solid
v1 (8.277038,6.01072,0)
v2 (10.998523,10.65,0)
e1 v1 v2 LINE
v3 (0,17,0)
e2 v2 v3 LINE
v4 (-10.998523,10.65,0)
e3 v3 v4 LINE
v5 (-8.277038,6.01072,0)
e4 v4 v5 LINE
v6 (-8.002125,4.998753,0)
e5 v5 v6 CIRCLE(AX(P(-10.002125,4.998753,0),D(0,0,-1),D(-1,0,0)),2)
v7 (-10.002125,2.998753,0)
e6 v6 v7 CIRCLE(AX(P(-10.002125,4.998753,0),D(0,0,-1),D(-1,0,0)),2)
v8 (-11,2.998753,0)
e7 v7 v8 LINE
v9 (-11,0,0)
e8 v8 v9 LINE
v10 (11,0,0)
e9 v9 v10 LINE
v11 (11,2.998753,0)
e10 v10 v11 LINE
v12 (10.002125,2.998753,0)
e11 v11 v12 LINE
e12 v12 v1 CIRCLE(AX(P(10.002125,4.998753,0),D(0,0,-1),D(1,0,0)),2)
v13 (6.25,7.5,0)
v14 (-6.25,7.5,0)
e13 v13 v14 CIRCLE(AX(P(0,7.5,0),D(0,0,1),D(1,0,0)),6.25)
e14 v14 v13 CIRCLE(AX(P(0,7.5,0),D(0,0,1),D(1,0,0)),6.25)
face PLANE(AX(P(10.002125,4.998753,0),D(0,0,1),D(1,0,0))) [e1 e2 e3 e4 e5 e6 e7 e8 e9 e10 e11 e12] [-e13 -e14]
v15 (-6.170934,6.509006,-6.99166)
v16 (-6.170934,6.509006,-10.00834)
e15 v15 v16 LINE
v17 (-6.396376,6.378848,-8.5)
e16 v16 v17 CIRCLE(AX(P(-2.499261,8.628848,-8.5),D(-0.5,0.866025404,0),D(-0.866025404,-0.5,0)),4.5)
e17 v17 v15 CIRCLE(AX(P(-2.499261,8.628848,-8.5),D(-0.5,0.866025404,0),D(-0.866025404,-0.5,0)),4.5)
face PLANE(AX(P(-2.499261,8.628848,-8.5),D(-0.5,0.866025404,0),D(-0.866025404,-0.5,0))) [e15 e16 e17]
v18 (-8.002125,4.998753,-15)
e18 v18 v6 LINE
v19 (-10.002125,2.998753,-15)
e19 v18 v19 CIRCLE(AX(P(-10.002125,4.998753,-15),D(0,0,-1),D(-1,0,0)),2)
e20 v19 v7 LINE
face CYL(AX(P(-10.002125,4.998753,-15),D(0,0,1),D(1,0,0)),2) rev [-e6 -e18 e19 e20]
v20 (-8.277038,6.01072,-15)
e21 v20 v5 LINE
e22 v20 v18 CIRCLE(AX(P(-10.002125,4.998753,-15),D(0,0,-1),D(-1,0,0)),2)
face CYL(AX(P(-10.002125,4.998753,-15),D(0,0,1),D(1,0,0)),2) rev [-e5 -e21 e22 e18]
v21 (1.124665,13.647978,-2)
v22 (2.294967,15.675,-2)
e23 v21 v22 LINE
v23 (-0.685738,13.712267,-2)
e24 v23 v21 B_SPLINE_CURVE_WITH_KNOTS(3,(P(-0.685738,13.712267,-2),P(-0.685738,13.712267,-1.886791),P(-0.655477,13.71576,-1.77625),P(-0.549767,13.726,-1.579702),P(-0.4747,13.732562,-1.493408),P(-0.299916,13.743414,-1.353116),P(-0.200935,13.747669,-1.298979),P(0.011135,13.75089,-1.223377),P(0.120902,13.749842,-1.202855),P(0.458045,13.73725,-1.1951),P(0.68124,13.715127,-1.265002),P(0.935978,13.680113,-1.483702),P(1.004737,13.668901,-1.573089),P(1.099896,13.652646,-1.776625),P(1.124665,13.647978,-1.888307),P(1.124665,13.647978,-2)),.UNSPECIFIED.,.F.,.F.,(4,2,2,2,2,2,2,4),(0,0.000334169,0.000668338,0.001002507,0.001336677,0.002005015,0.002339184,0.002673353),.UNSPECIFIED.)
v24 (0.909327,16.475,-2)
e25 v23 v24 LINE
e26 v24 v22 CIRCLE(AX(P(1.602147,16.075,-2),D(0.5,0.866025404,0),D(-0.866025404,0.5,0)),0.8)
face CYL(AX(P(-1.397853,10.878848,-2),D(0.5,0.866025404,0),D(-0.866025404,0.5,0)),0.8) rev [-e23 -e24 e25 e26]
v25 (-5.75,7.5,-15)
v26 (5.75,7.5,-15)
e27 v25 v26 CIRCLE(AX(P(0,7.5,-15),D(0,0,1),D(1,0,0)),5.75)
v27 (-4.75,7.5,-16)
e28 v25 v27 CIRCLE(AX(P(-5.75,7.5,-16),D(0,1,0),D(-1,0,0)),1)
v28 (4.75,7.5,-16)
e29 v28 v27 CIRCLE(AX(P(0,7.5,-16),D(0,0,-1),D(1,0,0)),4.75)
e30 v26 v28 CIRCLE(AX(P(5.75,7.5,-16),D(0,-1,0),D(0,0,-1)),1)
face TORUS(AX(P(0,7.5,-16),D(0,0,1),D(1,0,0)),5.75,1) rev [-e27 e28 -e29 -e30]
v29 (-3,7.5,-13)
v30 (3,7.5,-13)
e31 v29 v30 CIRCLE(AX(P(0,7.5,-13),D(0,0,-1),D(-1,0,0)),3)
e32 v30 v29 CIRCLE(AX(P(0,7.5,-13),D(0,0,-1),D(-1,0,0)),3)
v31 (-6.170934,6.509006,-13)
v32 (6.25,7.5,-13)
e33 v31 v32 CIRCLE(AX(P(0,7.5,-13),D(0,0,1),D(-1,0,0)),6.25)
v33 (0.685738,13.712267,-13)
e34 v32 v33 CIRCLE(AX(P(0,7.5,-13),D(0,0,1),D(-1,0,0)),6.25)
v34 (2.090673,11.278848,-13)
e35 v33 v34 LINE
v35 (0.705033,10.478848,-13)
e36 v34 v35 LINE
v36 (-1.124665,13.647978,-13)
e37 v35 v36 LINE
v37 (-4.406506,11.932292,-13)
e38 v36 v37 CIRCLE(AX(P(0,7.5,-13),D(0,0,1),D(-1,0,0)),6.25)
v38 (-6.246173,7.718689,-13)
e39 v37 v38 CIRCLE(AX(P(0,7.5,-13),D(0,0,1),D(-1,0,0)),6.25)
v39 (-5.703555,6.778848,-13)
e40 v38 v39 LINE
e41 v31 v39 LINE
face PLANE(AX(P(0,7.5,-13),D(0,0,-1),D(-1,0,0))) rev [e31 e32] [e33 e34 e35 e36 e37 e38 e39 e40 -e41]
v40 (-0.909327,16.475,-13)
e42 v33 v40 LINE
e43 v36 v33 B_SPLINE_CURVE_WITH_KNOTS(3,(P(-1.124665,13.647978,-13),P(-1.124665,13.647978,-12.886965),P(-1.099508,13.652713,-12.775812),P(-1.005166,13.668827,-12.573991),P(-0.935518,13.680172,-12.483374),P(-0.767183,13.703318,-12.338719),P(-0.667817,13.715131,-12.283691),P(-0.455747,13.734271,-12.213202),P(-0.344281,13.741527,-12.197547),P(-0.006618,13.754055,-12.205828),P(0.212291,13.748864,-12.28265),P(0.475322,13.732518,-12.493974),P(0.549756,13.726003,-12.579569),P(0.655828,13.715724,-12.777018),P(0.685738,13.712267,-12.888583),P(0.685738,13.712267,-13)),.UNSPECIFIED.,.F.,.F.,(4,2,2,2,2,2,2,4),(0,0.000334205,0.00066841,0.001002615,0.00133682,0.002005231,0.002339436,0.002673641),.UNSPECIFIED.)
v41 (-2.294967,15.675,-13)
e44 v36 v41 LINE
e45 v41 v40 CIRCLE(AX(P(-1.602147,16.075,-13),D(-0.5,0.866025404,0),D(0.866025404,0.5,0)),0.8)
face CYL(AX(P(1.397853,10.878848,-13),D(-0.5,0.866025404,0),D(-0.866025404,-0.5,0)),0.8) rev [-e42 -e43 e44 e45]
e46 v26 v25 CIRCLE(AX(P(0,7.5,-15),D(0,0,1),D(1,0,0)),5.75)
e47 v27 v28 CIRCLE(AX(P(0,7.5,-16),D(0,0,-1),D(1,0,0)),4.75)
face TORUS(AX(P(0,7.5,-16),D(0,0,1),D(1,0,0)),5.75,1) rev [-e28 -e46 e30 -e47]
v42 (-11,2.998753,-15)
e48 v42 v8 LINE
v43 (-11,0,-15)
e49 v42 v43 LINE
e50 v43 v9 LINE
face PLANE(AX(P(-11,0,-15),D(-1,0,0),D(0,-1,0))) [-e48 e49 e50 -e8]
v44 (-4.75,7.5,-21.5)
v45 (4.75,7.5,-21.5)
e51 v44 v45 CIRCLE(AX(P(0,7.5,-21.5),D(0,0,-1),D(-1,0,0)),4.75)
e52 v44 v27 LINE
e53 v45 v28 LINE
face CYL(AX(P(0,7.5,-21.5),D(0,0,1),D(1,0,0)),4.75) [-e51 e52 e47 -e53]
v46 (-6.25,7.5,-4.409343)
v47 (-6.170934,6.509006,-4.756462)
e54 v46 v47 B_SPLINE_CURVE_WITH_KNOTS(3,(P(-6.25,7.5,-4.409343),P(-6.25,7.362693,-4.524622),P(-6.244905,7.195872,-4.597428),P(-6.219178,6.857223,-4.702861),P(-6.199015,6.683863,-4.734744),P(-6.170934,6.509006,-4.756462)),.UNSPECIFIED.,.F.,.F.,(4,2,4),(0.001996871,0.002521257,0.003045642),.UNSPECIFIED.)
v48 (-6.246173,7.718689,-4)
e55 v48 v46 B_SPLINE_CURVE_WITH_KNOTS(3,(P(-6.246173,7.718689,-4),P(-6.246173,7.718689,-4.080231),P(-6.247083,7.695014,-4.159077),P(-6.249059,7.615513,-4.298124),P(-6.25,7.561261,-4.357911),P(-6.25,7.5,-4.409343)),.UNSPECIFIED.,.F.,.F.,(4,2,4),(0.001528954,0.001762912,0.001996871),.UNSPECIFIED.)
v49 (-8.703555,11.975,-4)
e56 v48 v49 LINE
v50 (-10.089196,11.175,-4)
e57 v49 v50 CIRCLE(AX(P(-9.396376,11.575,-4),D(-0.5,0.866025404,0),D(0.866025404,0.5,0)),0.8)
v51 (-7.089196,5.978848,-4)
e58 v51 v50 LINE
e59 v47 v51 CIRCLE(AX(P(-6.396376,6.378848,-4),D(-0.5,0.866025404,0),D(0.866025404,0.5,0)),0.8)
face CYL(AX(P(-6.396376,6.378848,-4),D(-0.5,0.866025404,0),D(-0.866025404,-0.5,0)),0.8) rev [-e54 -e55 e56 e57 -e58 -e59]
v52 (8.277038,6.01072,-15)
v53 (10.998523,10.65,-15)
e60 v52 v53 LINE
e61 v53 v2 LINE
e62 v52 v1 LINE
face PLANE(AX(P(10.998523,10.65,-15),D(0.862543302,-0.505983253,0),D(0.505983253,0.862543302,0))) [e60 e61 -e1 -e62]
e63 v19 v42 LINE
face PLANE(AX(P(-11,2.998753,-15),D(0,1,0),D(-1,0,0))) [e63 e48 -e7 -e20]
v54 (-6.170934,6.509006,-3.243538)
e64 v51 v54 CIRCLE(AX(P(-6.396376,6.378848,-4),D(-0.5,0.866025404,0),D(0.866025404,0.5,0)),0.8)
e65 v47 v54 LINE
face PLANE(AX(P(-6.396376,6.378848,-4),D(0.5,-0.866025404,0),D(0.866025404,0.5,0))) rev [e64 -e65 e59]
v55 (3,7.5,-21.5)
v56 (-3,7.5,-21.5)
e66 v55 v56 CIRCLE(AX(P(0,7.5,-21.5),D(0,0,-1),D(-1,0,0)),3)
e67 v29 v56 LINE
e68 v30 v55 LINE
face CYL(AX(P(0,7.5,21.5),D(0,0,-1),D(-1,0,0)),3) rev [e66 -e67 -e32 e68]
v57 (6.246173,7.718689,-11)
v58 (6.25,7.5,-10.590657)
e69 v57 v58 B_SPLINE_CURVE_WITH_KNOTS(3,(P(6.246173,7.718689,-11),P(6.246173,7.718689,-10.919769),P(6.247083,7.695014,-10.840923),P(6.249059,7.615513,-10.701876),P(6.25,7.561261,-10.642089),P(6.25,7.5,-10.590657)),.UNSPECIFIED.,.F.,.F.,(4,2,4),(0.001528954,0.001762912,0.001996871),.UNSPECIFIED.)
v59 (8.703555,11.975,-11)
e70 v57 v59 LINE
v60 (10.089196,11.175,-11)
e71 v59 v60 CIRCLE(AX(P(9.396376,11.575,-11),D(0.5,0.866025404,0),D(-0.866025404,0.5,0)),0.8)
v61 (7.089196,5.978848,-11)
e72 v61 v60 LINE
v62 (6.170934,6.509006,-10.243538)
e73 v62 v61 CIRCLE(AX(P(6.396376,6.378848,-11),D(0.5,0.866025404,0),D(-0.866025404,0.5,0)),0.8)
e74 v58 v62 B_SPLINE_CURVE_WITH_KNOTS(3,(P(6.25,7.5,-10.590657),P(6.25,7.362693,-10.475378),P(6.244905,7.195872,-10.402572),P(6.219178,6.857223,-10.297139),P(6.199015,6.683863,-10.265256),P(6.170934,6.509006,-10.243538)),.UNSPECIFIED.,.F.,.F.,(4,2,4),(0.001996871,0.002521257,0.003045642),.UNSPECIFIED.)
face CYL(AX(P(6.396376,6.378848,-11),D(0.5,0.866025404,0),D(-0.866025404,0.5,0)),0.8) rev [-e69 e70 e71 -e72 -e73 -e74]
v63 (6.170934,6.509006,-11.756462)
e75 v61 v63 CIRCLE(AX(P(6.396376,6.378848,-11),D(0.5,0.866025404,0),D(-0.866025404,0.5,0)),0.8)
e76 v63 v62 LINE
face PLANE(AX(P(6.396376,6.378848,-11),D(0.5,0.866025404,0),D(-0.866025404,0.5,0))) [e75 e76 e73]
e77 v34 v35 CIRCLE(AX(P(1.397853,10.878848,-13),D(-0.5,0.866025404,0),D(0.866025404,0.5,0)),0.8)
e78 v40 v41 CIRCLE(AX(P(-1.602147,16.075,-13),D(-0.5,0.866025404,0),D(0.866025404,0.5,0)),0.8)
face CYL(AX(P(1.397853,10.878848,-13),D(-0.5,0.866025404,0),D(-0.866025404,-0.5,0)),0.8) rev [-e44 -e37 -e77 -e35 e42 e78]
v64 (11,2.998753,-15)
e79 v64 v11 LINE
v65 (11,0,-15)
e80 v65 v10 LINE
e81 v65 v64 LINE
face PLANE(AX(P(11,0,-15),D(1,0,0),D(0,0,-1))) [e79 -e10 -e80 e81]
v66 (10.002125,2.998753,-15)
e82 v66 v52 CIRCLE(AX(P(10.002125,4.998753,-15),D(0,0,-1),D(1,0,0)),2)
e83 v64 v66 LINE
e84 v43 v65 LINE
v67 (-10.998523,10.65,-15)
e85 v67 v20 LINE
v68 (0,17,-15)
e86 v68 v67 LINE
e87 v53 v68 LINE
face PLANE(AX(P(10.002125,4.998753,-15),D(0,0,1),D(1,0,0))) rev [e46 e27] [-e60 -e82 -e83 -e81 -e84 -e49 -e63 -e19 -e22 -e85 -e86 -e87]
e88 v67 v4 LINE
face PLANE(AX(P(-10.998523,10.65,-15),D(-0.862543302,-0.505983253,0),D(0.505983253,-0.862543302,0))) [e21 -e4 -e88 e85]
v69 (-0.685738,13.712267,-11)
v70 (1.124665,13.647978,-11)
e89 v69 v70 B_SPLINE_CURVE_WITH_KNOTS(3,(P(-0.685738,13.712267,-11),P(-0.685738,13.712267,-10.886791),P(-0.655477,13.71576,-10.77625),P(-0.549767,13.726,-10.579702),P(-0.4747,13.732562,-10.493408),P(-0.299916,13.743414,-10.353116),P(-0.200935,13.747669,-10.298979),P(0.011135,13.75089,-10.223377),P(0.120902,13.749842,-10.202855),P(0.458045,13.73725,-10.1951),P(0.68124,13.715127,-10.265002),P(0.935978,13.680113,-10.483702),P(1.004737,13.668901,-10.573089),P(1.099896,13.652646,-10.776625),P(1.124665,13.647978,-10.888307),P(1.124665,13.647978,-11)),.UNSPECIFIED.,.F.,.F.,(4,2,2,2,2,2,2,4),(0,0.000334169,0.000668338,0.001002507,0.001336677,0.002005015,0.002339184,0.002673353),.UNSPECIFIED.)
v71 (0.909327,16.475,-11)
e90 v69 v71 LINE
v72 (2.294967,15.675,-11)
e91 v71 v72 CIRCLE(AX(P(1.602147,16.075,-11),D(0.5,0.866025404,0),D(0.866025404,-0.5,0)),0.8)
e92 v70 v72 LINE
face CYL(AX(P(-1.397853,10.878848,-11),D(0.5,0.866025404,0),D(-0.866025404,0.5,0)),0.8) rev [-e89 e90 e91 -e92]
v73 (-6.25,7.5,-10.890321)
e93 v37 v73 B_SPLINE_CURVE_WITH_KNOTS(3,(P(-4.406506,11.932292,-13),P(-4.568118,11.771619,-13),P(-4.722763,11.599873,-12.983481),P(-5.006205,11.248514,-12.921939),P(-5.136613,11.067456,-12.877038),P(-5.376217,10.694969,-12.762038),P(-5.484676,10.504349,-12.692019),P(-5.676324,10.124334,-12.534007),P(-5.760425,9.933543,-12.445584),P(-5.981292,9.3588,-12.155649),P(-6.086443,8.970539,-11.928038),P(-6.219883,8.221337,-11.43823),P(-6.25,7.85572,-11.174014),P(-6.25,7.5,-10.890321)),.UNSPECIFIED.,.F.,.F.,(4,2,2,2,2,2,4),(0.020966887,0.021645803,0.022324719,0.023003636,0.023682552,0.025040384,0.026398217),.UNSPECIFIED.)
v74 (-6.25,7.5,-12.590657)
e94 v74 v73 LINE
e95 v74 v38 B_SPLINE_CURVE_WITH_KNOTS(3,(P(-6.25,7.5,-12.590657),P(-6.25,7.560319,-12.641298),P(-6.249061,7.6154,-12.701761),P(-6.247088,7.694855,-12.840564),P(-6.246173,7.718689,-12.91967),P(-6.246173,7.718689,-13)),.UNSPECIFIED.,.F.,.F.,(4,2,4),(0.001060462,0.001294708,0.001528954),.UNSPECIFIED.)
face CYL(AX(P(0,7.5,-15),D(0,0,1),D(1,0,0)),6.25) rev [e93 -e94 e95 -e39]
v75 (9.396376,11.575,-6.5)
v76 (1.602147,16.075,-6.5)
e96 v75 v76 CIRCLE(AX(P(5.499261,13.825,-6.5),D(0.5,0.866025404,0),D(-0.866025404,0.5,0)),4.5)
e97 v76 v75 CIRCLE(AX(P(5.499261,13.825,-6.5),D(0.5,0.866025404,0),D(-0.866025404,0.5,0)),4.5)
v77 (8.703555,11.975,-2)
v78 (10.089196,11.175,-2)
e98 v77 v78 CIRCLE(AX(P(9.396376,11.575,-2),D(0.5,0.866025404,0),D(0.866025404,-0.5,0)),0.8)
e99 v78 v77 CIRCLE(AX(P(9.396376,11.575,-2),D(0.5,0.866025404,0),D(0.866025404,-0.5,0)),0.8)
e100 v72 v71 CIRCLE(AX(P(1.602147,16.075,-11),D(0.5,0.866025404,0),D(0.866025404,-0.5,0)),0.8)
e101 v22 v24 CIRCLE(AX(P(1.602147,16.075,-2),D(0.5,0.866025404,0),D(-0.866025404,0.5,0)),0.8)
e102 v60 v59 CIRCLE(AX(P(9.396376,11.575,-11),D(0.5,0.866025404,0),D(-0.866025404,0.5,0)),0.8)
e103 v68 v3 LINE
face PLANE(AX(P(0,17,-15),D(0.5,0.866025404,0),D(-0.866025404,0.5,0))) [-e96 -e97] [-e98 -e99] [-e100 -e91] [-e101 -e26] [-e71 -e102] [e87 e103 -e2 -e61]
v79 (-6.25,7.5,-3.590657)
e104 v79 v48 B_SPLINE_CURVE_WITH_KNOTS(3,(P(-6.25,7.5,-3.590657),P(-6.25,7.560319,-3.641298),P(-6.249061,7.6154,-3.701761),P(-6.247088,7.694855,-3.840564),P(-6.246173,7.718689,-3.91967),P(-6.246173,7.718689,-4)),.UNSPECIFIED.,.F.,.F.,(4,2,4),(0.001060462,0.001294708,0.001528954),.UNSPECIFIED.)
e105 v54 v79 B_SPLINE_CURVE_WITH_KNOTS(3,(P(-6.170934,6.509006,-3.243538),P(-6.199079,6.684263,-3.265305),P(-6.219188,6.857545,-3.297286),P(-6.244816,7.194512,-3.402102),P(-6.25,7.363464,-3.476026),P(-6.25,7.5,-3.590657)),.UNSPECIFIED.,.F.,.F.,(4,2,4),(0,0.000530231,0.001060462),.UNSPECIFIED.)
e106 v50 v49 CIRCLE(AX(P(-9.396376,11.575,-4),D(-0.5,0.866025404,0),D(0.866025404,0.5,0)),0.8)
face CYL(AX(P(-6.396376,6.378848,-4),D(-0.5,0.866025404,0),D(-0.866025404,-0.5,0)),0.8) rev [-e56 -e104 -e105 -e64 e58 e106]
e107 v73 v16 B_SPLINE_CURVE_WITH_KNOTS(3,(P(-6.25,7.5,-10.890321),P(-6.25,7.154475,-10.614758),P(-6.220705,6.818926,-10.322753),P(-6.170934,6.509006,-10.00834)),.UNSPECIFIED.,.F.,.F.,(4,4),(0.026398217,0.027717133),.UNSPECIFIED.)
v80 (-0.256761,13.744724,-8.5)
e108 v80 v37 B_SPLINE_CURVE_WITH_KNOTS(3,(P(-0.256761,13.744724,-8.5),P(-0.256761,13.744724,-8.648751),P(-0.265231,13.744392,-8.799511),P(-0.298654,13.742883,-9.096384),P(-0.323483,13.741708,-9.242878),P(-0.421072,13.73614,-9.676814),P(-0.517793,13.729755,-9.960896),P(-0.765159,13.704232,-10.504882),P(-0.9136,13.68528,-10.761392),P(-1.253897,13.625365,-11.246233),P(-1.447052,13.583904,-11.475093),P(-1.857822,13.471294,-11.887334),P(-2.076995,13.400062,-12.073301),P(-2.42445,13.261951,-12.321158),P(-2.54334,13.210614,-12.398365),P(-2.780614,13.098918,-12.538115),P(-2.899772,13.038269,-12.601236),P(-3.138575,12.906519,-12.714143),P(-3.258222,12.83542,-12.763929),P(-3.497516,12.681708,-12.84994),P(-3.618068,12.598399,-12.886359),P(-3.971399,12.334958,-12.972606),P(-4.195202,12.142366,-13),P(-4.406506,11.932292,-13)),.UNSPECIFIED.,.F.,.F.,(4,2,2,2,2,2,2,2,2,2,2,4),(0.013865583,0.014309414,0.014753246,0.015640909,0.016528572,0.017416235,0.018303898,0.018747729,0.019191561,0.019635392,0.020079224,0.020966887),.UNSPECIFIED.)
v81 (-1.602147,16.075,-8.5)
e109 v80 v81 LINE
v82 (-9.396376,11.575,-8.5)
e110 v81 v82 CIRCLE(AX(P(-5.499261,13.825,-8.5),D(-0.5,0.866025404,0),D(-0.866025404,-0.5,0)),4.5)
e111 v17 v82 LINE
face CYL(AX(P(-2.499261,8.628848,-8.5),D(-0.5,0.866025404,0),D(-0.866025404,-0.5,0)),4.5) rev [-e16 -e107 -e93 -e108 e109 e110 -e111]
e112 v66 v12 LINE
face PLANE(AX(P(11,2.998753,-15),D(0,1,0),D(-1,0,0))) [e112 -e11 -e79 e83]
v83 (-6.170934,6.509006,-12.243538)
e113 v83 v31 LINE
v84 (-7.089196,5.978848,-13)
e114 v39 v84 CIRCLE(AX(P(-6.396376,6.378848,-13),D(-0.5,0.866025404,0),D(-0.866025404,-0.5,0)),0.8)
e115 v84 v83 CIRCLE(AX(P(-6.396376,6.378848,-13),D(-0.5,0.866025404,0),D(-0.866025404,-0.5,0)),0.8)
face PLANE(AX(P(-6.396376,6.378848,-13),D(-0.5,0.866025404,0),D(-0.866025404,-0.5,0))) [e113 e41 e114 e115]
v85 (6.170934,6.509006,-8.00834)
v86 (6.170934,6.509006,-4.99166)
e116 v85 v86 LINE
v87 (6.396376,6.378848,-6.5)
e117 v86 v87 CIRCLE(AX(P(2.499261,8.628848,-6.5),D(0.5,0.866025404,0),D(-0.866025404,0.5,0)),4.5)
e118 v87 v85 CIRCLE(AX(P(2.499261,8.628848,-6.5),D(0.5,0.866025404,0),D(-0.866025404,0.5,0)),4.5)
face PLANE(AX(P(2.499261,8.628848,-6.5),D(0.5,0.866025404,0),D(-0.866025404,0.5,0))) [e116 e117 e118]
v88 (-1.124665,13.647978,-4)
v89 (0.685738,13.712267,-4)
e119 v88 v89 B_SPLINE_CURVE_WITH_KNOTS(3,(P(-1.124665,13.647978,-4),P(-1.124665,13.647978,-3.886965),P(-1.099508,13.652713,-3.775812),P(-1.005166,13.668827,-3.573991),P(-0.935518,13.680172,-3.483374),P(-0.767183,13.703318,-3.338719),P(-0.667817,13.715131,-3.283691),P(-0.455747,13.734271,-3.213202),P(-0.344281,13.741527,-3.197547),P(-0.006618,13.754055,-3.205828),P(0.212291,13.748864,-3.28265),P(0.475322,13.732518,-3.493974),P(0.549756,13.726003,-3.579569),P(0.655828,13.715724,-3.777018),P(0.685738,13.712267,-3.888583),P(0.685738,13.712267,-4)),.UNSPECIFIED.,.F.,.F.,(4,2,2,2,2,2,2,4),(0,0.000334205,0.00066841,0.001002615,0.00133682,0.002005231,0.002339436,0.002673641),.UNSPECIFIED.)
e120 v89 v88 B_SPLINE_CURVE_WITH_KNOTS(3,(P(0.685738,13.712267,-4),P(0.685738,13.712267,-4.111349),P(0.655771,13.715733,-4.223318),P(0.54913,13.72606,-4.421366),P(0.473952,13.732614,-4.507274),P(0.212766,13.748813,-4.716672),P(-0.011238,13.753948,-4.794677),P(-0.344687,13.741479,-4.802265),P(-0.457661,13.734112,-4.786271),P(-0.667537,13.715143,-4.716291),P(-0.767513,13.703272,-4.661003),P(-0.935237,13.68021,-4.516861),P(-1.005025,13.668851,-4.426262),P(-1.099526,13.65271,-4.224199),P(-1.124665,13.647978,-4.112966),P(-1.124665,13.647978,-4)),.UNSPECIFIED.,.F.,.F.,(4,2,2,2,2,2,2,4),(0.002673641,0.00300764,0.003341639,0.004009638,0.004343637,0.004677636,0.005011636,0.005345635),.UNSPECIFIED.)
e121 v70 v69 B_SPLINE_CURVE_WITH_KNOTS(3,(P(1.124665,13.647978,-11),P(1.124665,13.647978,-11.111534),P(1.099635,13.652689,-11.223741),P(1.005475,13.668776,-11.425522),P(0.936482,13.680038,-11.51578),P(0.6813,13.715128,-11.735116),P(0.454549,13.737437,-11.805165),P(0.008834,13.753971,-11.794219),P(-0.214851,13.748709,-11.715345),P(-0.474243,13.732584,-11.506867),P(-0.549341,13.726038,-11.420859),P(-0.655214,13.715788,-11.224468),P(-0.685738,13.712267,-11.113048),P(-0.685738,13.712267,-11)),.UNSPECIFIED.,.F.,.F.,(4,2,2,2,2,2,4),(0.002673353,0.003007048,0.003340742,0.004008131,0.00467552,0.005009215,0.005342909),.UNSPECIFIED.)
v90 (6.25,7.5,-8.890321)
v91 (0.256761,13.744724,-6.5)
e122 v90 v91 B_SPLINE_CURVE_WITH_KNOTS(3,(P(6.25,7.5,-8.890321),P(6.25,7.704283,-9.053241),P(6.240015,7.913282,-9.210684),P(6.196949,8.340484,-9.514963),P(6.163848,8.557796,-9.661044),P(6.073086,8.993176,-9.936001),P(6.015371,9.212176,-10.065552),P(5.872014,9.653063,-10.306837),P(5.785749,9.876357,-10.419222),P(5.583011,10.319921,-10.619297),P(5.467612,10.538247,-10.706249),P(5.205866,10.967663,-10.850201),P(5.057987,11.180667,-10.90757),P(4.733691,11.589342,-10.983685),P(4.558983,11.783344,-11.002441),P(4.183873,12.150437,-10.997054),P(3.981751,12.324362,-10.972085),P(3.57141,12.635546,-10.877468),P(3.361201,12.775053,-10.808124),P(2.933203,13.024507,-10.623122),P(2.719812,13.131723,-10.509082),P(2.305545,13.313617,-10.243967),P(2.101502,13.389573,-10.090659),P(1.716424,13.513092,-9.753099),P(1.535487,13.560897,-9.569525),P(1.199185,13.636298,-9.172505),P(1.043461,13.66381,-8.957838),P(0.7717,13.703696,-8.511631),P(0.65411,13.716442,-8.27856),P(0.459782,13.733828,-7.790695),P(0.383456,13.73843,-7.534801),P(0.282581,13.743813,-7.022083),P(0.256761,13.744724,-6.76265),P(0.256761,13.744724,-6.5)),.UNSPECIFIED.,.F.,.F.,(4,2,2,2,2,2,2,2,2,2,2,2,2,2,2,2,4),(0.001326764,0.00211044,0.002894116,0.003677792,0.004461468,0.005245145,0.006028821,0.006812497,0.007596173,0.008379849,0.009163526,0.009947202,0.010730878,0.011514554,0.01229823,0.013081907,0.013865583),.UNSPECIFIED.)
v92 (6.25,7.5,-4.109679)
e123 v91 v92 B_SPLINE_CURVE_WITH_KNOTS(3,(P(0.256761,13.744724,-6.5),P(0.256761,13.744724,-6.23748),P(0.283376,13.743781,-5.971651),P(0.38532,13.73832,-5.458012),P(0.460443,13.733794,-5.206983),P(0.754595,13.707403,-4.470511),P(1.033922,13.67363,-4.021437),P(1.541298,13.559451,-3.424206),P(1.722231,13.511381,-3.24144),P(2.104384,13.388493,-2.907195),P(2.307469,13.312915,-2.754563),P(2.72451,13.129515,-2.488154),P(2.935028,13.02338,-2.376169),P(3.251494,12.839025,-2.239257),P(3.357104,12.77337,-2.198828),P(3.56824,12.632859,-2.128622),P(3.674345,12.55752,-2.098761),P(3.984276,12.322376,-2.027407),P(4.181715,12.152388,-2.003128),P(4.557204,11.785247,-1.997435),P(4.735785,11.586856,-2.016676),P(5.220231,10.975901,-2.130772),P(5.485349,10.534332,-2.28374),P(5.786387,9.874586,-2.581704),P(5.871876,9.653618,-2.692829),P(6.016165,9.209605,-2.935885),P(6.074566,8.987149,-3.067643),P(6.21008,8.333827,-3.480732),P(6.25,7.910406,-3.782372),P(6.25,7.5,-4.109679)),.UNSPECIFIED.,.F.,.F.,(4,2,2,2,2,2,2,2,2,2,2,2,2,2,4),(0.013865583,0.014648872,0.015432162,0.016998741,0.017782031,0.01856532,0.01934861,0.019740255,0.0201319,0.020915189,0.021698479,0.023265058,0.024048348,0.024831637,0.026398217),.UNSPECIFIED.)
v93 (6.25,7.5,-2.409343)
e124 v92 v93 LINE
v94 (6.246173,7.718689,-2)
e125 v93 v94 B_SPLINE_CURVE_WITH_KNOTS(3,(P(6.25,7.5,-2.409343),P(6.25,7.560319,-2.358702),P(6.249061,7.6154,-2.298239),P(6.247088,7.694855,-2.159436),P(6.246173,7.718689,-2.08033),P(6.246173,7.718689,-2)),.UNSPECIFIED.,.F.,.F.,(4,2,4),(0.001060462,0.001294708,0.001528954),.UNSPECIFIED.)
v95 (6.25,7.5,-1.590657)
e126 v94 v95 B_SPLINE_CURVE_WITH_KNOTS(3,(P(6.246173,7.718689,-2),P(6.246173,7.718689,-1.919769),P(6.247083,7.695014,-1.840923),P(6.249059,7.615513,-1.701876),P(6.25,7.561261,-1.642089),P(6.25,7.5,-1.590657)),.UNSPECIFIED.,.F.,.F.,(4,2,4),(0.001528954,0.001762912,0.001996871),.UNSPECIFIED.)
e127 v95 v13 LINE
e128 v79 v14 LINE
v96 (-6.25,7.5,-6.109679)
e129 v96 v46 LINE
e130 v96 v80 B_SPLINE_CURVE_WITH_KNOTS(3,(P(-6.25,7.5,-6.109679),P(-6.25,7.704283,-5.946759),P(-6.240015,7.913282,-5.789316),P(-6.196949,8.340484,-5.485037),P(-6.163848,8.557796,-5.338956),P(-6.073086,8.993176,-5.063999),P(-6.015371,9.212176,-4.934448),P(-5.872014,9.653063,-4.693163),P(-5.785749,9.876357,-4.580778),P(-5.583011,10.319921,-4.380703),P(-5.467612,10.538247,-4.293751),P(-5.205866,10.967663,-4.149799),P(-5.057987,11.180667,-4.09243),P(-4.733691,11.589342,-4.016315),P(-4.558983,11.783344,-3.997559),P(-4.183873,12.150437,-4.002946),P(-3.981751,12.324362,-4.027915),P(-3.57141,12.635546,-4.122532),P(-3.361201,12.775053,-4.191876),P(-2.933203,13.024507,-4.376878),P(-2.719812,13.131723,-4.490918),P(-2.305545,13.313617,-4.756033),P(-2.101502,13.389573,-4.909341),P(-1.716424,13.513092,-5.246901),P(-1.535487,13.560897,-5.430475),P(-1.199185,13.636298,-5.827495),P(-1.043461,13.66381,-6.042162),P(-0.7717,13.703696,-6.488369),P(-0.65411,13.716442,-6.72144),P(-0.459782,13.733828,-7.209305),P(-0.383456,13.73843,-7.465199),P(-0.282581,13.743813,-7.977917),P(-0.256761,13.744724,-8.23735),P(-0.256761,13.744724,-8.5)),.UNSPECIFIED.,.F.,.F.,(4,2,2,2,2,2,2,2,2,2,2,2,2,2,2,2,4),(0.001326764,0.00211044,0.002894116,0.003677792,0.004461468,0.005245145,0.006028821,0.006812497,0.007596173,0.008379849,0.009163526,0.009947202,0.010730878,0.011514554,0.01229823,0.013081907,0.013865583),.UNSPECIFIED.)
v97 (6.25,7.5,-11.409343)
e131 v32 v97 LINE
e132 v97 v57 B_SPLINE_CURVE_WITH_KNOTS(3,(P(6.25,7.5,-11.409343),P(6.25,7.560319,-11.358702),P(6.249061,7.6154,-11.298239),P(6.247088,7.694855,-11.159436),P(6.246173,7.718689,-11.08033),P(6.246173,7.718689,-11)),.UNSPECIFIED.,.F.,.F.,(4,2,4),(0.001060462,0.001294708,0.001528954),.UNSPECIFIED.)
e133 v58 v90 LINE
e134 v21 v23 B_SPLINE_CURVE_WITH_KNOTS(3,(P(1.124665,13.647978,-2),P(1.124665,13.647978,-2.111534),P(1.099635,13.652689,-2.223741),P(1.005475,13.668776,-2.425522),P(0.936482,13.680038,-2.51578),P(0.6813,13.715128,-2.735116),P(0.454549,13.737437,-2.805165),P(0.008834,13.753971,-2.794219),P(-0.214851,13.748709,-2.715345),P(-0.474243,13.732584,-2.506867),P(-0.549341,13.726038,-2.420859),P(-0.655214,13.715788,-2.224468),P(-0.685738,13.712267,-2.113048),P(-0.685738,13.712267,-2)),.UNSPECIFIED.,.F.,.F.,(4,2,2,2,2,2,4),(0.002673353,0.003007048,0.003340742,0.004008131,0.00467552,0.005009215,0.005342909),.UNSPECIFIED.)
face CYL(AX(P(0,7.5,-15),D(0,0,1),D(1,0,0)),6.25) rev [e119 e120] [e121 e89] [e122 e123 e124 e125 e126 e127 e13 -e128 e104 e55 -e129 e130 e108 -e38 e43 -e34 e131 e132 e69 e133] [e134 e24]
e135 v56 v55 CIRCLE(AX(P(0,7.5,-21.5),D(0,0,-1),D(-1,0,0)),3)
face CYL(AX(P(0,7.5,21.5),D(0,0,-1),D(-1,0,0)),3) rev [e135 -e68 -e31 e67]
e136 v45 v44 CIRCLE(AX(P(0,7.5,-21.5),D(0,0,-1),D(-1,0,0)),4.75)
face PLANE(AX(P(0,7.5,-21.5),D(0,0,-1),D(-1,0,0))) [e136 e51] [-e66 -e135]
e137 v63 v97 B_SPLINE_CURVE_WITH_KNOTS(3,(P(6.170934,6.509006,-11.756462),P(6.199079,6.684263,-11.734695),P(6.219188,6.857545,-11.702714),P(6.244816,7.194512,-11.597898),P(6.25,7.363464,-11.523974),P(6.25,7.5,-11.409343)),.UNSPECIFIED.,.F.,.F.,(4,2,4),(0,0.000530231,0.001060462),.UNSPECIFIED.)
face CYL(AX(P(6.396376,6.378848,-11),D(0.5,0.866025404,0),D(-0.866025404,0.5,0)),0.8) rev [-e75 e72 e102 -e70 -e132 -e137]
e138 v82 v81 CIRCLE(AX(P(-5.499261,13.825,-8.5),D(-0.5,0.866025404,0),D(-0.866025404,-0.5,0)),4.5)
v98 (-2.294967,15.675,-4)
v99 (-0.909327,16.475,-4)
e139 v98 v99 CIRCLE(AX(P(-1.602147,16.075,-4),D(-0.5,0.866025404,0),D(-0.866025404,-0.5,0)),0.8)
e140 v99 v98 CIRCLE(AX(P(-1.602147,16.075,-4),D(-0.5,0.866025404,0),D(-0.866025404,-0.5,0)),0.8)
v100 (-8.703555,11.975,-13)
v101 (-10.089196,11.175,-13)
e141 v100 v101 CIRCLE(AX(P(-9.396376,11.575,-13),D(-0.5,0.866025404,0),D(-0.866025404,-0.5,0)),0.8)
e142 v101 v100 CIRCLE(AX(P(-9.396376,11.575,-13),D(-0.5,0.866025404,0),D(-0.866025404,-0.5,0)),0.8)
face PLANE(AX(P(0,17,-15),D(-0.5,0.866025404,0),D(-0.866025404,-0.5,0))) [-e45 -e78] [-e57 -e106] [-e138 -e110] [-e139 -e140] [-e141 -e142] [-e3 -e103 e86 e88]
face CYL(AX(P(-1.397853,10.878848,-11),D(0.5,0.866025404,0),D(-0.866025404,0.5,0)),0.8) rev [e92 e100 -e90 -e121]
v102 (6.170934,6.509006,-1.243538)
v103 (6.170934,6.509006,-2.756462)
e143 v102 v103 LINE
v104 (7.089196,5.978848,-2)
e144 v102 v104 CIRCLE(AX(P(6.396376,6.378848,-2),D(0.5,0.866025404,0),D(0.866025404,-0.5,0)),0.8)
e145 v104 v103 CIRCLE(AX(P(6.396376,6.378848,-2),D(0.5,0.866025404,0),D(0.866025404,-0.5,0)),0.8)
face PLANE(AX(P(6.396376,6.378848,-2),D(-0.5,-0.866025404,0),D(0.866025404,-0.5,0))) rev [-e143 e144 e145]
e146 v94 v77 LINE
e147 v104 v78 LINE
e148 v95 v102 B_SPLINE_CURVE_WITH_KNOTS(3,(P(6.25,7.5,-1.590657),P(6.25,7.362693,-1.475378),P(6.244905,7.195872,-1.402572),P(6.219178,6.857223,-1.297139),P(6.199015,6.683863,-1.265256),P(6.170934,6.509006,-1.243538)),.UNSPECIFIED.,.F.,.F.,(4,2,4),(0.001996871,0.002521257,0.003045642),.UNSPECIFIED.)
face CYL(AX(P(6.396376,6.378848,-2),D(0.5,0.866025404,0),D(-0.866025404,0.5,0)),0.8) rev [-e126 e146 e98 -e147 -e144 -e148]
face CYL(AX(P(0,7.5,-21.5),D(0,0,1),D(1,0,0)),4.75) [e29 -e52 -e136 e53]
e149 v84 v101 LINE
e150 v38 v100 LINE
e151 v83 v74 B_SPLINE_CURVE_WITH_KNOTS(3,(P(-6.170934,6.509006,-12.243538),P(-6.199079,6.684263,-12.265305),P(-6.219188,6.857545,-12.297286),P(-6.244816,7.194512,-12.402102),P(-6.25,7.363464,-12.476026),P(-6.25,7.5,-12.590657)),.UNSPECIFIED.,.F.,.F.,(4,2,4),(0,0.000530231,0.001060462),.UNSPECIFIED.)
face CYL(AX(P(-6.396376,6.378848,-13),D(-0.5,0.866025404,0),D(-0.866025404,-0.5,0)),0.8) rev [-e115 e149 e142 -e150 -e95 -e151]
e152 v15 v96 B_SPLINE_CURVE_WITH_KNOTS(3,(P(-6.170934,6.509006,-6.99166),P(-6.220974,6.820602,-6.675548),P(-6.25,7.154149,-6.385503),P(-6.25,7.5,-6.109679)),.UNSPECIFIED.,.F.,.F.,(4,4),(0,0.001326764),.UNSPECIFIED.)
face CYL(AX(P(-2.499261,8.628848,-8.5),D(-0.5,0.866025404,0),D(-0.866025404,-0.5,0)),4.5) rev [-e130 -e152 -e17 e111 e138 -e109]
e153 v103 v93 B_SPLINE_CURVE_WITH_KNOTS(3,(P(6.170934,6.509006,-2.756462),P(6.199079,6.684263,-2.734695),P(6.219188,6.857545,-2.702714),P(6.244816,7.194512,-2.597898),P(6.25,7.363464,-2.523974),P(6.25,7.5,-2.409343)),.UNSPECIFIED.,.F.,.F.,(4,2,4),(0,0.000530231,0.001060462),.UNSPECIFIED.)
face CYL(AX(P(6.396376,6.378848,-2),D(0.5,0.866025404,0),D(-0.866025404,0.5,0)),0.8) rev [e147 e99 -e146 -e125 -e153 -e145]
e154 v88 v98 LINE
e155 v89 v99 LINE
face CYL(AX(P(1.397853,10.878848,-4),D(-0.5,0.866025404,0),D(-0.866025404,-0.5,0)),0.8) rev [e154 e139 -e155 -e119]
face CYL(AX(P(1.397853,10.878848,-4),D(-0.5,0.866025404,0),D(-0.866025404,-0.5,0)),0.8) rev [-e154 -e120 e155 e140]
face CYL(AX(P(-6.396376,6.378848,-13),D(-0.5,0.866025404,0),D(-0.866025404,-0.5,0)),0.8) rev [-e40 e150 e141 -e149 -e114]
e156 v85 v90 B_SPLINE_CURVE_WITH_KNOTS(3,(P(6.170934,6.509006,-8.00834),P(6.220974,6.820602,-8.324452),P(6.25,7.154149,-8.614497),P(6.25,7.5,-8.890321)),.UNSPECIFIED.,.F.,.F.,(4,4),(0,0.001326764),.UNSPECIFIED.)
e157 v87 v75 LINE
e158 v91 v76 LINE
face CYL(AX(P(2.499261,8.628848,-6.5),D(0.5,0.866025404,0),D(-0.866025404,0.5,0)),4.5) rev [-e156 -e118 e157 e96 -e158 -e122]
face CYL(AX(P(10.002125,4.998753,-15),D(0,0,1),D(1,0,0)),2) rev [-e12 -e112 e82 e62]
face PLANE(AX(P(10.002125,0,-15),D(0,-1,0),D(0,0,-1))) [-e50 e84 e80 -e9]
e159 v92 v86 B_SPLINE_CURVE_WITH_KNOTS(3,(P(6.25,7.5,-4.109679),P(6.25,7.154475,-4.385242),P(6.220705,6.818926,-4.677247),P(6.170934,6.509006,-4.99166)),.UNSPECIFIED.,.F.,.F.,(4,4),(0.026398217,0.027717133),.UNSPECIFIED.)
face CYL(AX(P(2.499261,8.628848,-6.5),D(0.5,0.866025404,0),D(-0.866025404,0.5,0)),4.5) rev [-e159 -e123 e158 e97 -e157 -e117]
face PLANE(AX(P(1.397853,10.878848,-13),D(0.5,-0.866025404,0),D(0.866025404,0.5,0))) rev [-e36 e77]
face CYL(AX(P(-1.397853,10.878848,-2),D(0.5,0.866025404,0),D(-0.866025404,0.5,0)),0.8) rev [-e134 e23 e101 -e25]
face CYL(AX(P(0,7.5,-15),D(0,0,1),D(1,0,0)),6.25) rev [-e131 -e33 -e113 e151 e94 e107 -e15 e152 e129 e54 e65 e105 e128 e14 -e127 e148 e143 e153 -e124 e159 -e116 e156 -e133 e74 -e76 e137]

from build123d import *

# Parameters (mm, degrees)
HOUSING_PROFILE_SKETCH_R  = 6.25
HOUSING_BODY_DEPTH        = 15
CYLINDRICAL_BOSS_SKETCH_R = 4.75
CYLINDRICAL_BOSS_DEPTH    = 6.5
BOSS_START                = -2
BOSS_COLLAR_SKETCH_R      = 6.25
BOSS_COLLAR_DEPTH         = 2
THROUGH_BORE_SKETCH_R     = 3
THROUGH_BORE_DEPTH        = 43
FACE_HOLES_A_SKETCH_R     = 4.5
FACE_HOLES_A_SKETCH_R_2   = 0.8
FACE_HOLES_A_DEPTH        = 6
FACE_HOLES_B_SKETCH_R     = 4.5
FACE_HOLES_B_SKETCH_R_2   = 0.8
FACE_HOLES_B_DEPTH        = 6
EDGE_FILLET_R1_R          = 1


with BuildPart() as part:
    # Housing Profile Sketch → Housing Body (new body)
    with BuildSketch(Plane.XY):
        with BuildLine():
            Line((0, 17), (-10.998522628, 10.65))
            Line((-10.998522628, 10.65), (-8.277038378, 6.010719954))
            ThreePointArc((-8.277038378, 6.010719954), (-8.26662318, 4.004754709), (-10.002124982, 2.998753448))
            Line((-10.002124982, 2.998753448), (-11, 2.998753448))
            Line((-11, 2.998753448), (-11, 0))
            Line((-11, 0), (-10.002124982, 0))
            Line((-10.002124982, 0), (10.002124982, 0))
            Line((10.002124982, 0), (11, 0))
            Line((11, 0), (11, 2.998753448))
            Line((11, 2.998753448), (10.002124982, 2.998753448))
            ThreePointArc((10.002124982, 2.998753448), (8.26662318, 4.004754709), (8.277038378, 6.010719954))
            Line((8.277038378, 6.010719954), (10.998522628, 10.65))
            Line((10.998522628, 10.65), (0, 17))
        make_face()
        with Locations((0, 7.5)):
            Circle(HOUSING_PROFILE_SKETCH_R, mode=Mode.SUBTRACT)
    extrude(amount=-HOUSING_BODY_DEPTH)



with BuildPart() as body_2:
    # Cylindrical Boss Sketch → Cylindrical Boss (new body)
    with BuildSketch(Plane(origin=(0, 0, -15), x_dir=(-1, 0, 0), z_dir=(0, 0, -1))):
        with Locations(Location((0, 7.5, 0), (0, 0, 180))):
            Circle(CYLINDRICAL_BOSS_SKETCH_R)
    extrude(amount=CYLINDRICAL_BOSS_DEPTH)


with BuildPart() as part_1:
    add(part.part)

    add(body_2.part)  # Boss Collar merges body 2
    # Boss Collar Sketch → Boss Collar (add)
    with BuildSketch(Plane(origin=(0, 0, -15), x_dir=(-1, 0, 0), z_dir=(0, 0, -1)).offset(BOSS_START)):
        with Locations(Location((0, 7.5, 0), (0, 0, 180))):
            Circle(BOSS_COLLAR_SKETCH_R)
    extrude(amount=BOSS_COLLAR_DEPTH)

    # Through Bore Sketch → Through Bore (cut)
    with BuildSketch(Plane(origin=(0, 0, -21.5), x_dir=(-1, 0, 0), z_dir=(0, 0, -1))):
        with Locations((0, 7.5)):
            Circle(THROUGH_BORE_SKETCH_R)
    extrude(amount=-THROUGH_BORE_DEPTH, mode=Mode.SUBTRACT)

    # Face Holes A Sketch → Face Holes A (cut)
    with BuildSketch(Plane(origin=(7.361215932, 12.75, 0), x_dir=(0.8660254037844394, -0.4999999999999988, 0), z_dir=(0.4999999999999988, 0.8660254037844394, 0))):
        with Locations(Location((-2.15, 6.5, 0), (0, 0, 180))):
            Circle(FACE_HOLES_A_SKETCH_R)
        with Locations(Location((2.35, 11, 0), (0, 0, 180))):
            Circle(FACE_HOLES_A_SKETCH_R_2)
        with Locations(Location((2.35, 2, 0), (0, 0, 149.224237469))):
            Circle(FACE_HOLES_A_SKETCH_R_2)
        with Locations(Location((-6.65, 2, 0), (0, 0, 180))):
            Circle(FACE_HOLES_A_SKETCH_R_2)
        with Locations(Location((-6.65, 11, 0), (0, 0, 180))):
            Circle(FACE_HOLES_A_SKETCH_R_2)
    extrude(amount=-FACE_HOLES_A_DEPTH, mode=Mode.SUBTRACT)

    # Face Holes B Sketch → Face Holes B (cut)
    with BuildSketch(Plane(origin=(-7.361215932, 12.75, 0), x_dir=(0.8660254037844403, 0.4999999999999971, 0), z_dir=(-0.49999999999999717, 0.8660254037844404, 0))):
        with Locations(Location((2.15, 8.5, 0), (0, 0, 180))):
            Circle(FACE_HOLES_B_SKETCH_R)
        with Locations(Location((-2.35, 13, 0), (0, 0, 180))):
            Circle(FACE_HOLES_B_SKETCH_R_2)
        with Locations((6.65, 13)):
            Circle(FACE_HOLES_B_SKETCH_R_2)
        with Locations(Location((6.65, 4, 0), (0, 0, 180))):
            Circle(FACE_HOLES_B_SKETCH_R_2)
        with Locations(Location((-2.35, 4, 0), (0, 0, 71.010406817))):
            Circle(FACE_HOLES_B_SKETCH_R_2)
    extrude(amount=-FACE_HOLES_B_DEPTH, mode=Mode.SUBTRACT)

    # Edge Fillet R1
    edge_fillet_r1_edges = [part_1.edges().sort_by_distance(p)[0] for p in [
        (-4.75, 7.5, -15),
    ]]
    fillet(edge_fillet_r1_edges, radius=EDGE_FILLET_R1_R)


solid = part_1.part
